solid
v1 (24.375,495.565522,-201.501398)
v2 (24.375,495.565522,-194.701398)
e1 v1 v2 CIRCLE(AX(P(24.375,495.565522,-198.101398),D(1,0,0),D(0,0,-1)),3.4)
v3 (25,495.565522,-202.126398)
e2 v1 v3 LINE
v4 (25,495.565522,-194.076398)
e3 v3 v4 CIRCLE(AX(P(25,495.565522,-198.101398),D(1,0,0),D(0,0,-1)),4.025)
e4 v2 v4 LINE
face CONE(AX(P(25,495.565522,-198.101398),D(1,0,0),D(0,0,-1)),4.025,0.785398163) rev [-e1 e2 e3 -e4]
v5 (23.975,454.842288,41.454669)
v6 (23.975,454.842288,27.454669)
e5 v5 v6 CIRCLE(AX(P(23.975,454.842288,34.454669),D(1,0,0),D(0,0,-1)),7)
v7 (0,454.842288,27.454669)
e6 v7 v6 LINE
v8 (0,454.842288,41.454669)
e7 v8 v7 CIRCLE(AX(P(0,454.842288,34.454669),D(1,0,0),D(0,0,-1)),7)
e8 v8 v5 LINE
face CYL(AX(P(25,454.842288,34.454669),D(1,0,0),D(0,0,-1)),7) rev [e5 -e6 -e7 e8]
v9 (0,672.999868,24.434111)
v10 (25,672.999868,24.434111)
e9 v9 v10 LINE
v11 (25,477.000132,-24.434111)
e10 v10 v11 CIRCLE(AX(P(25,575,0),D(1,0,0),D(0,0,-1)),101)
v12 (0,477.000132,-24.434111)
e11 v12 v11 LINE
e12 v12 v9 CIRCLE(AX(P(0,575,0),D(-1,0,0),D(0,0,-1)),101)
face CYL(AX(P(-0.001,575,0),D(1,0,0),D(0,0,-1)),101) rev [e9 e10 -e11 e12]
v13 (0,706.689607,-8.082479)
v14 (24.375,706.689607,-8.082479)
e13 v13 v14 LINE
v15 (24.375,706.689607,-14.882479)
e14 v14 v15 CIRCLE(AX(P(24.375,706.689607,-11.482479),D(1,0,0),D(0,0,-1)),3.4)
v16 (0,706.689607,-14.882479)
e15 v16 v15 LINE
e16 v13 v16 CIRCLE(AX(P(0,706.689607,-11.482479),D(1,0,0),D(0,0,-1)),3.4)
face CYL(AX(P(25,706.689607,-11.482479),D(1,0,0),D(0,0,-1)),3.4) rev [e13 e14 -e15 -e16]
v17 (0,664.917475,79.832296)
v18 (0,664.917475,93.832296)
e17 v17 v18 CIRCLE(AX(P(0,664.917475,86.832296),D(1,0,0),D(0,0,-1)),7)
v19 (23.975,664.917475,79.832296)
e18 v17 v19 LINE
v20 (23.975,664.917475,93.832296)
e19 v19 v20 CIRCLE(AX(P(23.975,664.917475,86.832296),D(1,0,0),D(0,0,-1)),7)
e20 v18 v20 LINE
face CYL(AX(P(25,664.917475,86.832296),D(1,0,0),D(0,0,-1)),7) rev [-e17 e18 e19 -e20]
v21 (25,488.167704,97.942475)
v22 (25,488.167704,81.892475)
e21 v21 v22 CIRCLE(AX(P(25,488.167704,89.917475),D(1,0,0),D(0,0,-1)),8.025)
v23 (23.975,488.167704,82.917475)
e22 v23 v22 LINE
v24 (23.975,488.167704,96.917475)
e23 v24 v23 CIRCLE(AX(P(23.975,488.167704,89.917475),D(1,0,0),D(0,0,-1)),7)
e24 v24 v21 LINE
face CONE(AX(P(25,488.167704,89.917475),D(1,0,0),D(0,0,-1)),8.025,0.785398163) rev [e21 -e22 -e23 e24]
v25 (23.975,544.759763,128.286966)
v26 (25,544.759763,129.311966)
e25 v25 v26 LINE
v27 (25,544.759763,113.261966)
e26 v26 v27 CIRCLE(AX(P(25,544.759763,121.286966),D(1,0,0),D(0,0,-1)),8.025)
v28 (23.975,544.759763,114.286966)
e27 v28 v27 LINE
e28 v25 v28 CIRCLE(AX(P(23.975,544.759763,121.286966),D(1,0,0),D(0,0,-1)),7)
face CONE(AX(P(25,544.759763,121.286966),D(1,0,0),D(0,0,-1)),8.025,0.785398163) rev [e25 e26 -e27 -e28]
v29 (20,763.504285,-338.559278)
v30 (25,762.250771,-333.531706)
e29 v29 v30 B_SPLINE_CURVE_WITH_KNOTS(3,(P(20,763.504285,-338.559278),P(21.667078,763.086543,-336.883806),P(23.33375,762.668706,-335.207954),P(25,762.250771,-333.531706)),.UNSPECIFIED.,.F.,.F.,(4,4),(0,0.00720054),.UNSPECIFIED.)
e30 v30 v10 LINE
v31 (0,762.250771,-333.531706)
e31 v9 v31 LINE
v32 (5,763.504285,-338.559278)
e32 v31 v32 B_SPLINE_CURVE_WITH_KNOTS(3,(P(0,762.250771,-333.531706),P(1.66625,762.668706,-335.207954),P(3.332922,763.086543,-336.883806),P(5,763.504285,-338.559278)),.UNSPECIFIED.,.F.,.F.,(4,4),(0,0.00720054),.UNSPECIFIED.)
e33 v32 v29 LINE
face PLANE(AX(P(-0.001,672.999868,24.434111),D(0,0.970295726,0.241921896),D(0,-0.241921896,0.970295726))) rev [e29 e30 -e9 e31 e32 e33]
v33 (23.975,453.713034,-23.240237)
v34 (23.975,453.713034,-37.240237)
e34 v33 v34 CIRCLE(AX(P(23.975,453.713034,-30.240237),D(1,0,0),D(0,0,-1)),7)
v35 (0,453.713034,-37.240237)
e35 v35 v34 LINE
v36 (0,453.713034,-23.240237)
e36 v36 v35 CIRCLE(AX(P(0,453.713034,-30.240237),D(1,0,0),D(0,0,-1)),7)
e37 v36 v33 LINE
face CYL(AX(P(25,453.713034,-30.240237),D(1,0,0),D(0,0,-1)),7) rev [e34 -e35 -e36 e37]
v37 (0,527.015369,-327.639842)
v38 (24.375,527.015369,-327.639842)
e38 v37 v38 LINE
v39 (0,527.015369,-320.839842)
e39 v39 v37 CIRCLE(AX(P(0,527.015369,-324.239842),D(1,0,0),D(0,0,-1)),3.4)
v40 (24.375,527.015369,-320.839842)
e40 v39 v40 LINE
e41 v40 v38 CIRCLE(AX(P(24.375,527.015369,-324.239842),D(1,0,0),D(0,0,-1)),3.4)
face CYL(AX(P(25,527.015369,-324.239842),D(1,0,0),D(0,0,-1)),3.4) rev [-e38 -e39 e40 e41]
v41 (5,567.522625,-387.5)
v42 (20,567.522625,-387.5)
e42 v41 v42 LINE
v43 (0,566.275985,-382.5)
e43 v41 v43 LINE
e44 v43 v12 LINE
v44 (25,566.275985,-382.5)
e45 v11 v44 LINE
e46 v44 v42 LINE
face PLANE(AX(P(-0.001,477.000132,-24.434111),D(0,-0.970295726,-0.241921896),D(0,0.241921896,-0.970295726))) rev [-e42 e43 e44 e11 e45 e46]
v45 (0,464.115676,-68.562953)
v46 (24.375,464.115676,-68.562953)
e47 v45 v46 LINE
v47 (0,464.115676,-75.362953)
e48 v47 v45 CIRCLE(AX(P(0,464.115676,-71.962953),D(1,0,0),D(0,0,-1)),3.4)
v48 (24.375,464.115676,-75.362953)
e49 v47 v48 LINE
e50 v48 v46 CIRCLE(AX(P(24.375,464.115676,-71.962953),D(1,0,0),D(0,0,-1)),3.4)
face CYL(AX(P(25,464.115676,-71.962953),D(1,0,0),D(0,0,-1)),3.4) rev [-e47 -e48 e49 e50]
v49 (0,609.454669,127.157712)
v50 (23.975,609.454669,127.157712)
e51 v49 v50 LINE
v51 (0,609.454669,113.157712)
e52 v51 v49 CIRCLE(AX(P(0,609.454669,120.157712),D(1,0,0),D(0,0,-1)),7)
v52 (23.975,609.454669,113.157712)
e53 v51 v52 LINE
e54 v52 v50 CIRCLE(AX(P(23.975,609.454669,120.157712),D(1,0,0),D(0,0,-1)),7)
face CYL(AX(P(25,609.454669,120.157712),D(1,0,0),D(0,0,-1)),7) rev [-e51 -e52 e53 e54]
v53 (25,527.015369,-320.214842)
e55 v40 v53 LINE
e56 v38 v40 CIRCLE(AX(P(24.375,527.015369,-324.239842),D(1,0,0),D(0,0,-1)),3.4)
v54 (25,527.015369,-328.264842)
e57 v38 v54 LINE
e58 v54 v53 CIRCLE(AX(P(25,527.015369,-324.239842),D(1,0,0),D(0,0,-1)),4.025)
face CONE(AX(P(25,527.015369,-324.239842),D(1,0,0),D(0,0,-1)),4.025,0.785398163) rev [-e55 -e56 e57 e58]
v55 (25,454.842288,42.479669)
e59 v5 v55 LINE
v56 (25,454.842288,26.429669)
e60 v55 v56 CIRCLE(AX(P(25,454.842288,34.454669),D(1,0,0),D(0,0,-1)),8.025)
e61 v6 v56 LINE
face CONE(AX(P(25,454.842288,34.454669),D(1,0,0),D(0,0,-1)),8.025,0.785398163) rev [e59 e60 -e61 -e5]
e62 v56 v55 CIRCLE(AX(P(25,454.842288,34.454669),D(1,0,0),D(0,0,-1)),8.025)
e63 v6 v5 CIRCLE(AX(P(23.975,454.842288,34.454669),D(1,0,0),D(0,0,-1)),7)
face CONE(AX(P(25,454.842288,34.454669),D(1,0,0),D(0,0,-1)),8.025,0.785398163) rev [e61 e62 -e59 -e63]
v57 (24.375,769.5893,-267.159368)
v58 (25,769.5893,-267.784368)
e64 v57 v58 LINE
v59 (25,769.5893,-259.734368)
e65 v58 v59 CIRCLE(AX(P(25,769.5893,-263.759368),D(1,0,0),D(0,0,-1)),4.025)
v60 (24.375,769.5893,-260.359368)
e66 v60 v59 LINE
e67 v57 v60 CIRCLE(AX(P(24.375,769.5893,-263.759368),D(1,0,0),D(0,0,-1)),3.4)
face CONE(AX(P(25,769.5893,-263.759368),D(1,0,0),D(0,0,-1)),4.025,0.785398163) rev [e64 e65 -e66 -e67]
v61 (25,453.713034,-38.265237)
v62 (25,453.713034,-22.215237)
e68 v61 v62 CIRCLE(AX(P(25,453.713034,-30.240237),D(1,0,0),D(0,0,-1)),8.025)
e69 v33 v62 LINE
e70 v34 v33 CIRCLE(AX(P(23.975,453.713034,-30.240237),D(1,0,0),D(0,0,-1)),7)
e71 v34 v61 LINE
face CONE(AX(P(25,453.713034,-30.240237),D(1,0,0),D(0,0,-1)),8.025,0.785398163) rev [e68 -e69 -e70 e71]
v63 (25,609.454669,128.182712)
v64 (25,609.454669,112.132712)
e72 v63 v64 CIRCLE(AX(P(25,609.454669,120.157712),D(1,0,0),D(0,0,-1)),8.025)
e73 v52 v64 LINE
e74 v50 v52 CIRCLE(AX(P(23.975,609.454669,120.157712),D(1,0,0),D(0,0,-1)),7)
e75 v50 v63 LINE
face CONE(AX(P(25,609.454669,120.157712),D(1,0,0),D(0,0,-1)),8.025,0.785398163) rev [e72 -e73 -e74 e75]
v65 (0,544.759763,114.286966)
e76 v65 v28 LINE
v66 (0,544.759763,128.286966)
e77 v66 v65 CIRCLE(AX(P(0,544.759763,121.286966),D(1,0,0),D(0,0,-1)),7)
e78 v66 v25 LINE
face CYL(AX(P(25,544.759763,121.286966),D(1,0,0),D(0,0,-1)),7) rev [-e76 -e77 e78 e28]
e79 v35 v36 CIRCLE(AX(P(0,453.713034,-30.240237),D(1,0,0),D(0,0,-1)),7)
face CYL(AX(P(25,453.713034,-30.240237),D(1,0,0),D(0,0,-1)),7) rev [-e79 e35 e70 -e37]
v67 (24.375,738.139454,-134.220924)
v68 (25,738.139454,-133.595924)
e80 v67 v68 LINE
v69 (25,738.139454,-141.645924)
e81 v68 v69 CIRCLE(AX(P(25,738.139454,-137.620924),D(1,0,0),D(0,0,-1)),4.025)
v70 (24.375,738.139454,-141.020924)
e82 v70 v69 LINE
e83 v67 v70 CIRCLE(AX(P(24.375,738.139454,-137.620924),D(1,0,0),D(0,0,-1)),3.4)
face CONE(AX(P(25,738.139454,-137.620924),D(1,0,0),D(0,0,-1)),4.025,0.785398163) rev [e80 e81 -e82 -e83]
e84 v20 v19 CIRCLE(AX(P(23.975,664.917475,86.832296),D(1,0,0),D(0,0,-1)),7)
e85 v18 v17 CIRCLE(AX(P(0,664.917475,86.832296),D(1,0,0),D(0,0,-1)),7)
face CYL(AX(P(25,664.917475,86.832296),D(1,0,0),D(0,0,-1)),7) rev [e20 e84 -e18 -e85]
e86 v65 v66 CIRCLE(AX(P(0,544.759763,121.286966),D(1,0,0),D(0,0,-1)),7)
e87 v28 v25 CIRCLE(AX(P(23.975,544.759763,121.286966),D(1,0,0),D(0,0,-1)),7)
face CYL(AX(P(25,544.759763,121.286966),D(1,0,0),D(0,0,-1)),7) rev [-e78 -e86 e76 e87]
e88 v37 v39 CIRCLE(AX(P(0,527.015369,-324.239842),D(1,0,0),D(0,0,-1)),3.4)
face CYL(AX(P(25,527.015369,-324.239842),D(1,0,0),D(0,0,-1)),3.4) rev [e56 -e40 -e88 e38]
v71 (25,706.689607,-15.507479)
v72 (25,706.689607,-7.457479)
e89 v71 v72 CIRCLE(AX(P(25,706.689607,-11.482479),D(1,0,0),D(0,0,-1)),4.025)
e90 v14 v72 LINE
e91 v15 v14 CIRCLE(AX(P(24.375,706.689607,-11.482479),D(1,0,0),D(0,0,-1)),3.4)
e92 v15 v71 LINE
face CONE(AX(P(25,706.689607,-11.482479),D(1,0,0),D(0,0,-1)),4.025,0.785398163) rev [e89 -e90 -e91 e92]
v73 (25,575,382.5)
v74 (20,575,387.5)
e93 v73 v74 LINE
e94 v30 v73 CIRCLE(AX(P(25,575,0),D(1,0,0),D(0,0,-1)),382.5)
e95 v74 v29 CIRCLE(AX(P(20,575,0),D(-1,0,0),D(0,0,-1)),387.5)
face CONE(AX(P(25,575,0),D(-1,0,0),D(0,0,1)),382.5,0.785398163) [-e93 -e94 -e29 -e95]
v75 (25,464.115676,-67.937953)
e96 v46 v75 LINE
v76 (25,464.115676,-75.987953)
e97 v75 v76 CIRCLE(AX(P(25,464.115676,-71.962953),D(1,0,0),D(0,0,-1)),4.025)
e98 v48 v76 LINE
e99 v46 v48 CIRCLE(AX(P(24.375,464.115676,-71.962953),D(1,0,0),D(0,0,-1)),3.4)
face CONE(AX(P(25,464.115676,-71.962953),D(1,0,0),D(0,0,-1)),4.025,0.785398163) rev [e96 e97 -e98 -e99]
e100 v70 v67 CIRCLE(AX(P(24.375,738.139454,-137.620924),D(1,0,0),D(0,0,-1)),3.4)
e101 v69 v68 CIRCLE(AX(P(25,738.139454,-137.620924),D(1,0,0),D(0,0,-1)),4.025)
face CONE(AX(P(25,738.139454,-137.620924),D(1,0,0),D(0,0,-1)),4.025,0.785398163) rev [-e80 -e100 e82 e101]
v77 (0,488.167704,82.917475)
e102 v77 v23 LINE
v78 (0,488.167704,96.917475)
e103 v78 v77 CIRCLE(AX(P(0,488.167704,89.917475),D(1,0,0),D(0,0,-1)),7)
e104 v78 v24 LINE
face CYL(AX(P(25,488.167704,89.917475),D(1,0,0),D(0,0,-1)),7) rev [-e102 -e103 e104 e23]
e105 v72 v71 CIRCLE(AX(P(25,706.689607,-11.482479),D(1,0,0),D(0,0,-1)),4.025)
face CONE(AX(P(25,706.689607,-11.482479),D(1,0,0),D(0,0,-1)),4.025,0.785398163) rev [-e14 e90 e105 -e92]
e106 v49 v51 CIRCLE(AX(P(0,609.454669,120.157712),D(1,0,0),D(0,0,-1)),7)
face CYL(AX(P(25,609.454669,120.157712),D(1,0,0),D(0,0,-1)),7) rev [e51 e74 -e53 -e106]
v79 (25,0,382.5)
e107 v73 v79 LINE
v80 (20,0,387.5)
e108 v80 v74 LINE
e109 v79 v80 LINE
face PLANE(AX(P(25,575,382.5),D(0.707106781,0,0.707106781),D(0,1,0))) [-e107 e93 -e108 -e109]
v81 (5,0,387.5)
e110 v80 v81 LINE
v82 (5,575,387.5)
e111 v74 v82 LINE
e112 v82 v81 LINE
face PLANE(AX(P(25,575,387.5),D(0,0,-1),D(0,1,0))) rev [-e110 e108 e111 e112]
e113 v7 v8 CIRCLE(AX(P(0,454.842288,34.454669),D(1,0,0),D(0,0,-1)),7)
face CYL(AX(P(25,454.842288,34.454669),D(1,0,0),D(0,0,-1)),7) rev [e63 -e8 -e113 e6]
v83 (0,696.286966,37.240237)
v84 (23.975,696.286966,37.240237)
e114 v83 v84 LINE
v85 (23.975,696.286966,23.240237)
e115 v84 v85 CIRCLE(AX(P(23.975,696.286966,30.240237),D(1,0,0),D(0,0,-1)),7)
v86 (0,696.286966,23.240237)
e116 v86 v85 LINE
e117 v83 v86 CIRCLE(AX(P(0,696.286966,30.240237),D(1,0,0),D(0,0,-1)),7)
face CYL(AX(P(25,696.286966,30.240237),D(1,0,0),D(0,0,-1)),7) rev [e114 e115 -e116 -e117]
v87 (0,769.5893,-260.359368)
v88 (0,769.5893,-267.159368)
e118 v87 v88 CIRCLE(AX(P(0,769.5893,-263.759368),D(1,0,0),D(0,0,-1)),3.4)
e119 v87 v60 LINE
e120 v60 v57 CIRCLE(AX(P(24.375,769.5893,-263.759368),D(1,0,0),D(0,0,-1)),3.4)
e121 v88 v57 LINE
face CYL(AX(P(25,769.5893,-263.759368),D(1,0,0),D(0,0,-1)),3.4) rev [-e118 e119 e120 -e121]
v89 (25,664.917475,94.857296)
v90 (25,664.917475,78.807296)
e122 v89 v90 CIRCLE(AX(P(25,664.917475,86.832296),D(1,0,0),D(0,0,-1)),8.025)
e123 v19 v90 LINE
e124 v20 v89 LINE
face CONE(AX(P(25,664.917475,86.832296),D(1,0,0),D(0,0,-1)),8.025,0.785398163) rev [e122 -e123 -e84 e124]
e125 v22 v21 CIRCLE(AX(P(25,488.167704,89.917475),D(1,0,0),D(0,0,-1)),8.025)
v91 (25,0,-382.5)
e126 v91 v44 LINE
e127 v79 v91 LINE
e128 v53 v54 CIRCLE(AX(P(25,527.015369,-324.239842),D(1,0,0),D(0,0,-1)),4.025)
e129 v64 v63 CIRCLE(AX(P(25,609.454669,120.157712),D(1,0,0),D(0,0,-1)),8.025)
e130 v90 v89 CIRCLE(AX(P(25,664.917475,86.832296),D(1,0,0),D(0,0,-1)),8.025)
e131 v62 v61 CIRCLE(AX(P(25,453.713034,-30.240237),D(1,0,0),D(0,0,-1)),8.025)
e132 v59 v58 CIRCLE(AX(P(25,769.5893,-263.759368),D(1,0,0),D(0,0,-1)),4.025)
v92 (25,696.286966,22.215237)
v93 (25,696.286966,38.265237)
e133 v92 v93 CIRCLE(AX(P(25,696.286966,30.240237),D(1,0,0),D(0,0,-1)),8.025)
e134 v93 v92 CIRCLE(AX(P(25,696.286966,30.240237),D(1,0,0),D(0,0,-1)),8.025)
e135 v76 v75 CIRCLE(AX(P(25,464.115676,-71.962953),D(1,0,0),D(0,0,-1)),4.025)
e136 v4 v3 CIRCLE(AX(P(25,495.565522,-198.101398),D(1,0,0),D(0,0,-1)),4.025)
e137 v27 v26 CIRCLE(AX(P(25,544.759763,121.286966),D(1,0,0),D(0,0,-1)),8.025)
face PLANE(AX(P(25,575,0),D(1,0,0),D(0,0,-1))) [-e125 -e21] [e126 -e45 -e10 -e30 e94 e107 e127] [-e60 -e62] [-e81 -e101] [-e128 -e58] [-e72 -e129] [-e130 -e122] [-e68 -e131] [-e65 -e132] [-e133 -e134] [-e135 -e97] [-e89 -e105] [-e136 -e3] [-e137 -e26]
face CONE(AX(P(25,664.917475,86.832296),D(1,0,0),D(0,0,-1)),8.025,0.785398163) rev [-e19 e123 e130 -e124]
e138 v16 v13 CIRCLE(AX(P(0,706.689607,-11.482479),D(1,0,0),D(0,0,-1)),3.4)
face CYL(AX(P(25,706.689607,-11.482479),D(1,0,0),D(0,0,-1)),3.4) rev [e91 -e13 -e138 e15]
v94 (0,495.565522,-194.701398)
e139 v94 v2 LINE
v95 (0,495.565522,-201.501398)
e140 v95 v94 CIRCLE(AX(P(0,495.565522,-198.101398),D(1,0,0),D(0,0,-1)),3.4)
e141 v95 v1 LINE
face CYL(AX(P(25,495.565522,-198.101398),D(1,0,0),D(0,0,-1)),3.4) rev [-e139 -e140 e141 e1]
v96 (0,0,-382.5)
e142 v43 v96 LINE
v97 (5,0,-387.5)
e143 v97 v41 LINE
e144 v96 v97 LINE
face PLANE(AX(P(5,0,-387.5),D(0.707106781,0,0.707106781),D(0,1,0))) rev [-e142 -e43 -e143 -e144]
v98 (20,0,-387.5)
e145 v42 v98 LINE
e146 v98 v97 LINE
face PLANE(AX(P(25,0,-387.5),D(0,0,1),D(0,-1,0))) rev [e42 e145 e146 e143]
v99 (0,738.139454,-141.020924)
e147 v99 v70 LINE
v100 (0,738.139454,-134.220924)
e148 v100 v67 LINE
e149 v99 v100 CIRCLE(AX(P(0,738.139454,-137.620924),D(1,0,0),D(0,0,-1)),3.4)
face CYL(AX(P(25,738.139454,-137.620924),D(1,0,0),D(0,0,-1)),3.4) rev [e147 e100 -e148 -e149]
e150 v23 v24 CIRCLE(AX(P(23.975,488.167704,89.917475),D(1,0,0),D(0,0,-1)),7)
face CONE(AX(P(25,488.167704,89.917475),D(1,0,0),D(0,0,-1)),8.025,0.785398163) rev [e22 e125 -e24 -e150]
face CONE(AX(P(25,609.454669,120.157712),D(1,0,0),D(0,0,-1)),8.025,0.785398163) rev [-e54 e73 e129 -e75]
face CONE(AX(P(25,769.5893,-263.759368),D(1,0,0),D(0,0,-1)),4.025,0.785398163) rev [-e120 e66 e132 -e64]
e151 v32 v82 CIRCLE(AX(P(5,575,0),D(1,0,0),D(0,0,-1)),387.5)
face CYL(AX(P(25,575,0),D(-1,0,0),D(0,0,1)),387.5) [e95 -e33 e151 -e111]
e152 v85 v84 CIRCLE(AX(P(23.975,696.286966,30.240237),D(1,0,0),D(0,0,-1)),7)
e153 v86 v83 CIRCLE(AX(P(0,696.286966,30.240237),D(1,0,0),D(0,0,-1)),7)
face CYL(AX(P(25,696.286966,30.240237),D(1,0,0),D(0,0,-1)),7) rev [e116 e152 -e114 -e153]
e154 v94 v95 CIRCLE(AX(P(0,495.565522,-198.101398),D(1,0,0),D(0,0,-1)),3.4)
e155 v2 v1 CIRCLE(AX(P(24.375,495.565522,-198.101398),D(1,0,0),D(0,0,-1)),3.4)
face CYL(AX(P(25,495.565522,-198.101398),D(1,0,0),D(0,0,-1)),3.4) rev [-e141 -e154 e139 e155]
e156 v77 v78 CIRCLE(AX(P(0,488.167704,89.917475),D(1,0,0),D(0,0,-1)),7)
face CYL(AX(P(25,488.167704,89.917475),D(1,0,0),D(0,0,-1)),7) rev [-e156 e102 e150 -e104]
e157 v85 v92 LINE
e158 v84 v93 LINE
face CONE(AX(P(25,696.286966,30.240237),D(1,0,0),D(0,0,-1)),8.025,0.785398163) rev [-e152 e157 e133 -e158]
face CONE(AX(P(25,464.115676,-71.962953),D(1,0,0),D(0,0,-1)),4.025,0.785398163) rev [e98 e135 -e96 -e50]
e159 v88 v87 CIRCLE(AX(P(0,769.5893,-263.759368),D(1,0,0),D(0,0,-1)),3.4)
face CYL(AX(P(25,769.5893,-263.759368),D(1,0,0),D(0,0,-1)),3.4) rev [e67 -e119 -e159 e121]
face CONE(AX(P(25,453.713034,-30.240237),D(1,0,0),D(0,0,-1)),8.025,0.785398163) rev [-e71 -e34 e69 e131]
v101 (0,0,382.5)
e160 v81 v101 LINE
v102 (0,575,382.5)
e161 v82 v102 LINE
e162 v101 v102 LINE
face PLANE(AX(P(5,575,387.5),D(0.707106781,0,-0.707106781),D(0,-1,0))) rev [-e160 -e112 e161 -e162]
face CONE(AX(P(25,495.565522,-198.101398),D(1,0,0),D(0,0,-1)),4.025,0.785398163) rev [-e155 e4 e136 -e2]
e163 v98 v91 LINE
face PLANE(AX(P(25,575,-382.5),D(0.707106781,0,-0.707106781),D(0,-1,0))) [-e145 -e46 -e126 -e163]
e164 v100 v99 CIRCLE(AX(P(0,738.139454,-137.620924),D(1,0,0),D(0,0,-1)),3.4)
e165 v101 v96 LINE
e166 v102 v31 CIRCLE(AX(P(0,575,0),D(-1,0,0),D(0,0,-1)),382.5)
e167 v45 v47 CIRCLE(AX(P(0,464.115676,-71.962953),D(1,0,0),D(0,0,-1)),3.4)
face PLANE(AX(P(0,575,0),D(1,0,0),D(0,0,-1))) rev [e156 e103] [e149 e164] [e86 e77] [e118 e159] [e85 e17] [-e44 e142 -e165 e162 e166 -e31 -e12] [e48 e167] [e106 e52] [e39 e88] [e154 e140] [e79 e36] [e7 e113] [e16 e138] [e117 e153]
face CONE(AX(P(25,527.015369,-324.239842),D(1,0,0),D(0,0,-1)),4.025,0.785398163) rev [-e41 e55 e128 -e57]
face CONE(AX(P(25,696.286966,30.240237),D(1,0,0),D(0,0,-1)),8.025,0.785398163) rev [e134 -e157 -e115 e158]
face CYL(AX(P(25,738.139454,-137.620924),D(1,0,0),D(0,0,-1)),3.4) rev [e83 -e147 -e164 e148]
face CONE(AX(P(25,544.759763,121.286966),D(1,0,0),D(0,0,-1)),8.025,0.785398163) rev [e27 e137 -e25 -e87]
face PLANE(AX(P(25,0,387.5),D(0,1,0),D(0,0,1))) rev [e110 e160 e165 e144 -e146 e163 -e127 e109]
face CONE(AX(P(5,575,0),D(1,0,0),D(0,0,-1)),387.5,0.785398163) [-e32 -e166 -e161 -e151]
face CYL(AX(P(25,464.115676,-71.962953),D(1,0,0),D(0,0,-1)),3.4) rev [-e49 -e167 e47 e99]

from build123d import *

# Parameters (mm, degrees)
BOSS_EXTRUDE1_DEPTH          = 25
CUT_EXTRUDE1_REACH           = 1039.876
M16_TAPPED_HOLE1_D           = 14
M16_TAPPED_HOLE1_CSINK_D     = 16.05
M16_TAPPED_HOLE1_CSINK_ANGLE = 90
CIRPATTERN1_COUNT            = 12
M8_TAPPED_HOLE1_D            = 6.8
M8_TAPPED_HOLE1_CSINK_D      = 8.05
M8_TAPPED_HOLE1_CSINK_ANGLE  = 90
LPATTERN1_COUNT              = 3
LPATTERN1_PITCH              = 130
MIRROR1_COPY_1_D             = 6.8
MIRROR1_COPY_1_CSINK_D       = 8.05
MIRROR1_COPY_1_CSINK_ANGLE   = 90
MIRROR1_COPY_2_D             = 6.8
MIRROR1_COPY_2_CSINK_D       = 8.05
MIRROR1_COPY_2_CSINK_ANGLE   = 90
CHAMFER1_SIZE                = 5


with BuildPart() as part:
    # Sketch1 → Boss-Extrude1 (new body)
    with BuildSketch(Plane(origin=(0, 0, 0), x_dir=(0, 0, -1), z_dir=(1, 0, 0))):
        with BuildLine():
            Line((-387.5, 575), (-387.5, 0))
            Line((-387.5, 0), (387.5, 0))
            Line((387.5, 0), (387.5, 575))
            ThreePointArc((387.5, 575), (0, 962.5), (-387.5, 575))
        make_face()
    extrude(amount=BOSS_EXTRUDE1_DEPTH)

    # Sketch2 → Cut-Extrude1 (cut, up to next)
    with BuildSketch(Plane(origin=(25, 0, 0), x_dir=(0, 0, -1), z_dir=(1, 0, 0)), mode=Mode.PRIVATE) as cut_extrude1_sk1:
        with BuildLine():
            Line((-24.434111456, 672.999868354), (338.559277668, 763.504285109))
            ThreePointArc((338.559277668, 763.504285109), (375.065307711, 672.37692207), (387.5, 575))
            Line((387.5, 575), (387.5, 567.522624537))
            Line((387.5, 567.522624537), (24.434111456, 477.000131646))
            ThreePointArc((24.434111456, 477.000131646), (-97.999868354, 550.565888544), (-24.434111456, 672.999868354))
        make_face()
    cut_extrude1_tool1 = extrude(cut_extrude1_sk1.sketch, amount=-CUT_EXTRUDE1_REACH, mode=Mode.PRIVATE) & part.part
    add(cut_extrude1_tool1.solids().sort_by_distance((25, 611.611981, -146.843429))[0], mode=Mode.SUBTRACT)

    # M16 Tapped Hole1 (through all)
    with Locations(Plane(origin=(25, 696.286965784, 30.24023695), x_dir=(0, 0, 1), z_dir=(1, 0, 0))):
        with Locations((0, 0)):
            m16_tapped_hole1 = CounterSinkHole(M16_TAPPED_HOLE1_D / 2, M16_TAPPED_HOLE1_CSINK_D / 2, counter_sink_angle=M16_TAPPED_HOLE1_CSINK_ANGLE)

    # CirPattern1: M16 Tapped Hole1 ×12 about axis, 5 skipped
    cirpattern1_axis = Axis((-0.001, 575, 0), (-1, 0, 0))
    add([m16_tapped_hole1.rotate(cirpattern1_axis, i * 360 / CIRPATTERN1_COUNT) for i in range(1, CIRPATTERN1_COUNT) if i not in (1, 2, 3, 4, 5)], mode=Mode.SUBTRACT)

    # M8 Tapped Hole1 (through all)
    with Locations(Plane(origin=(25, 706.689607295, -11.48247928), x_dir=(0, 0, 1), z_dir=(1, 0, 0))):
        with Locations((0, 0)):
            m8_tapped_hole1 = CounterSinkHole(M8_TAPPED_HOLE1_D / 2, M8_TAPPED_HOLE1_CSINK_D / 2, counter_sink_angle=M8_TAPPED_HOLE1_CSINK_ANGLE)

    # LPattern1: M8 Tapped Hole1 ×3
    with Locations(*[Vector(0, 0.24192189559966076, -0.9702957262759982) * (i * LPATTERN1_PITCH) for i in range(1, LPATTERN1_COUNT)]):
        add(m8_tapped_hole1, mode=Mode.SUBTRACT)

    # Mirror1: M8 Tapped Hole1 across plane
    add(m8_tapped_hole1.mirror(Plane(origin=(0, 541.347432947, 134.973074301), x_dir=(0, -0.24192189559966135, 0.970295726275998), z_dir=(0, 0.9702957262759981, 0.24192189559966135))), mode=Mode.SUBTRACT)

    # Mirror1 copy 1 (through all)
    with Locations(Plane(origin=(25, 495.565522155, -198.101397596), x_dir=(0, -0.4694715627858792, 0.8829475928589331), z_dir=(1, 0, 0))):
        with Locations((0, 0)):
            CounterSinkHole(MIRROR1_COPY_1_D / 2, MIRROR1_COPY_1_CSINK_D / 2, counter_sink_angle=MIRROR1_COPY_1_CSINK_ANGLE)

    # Mirror1 copy 2 (through all)
    with Locations(Plane(origin=(25, 527.015368582, -324.239842012), x_dir=(0, -0.4694715627858792, 0.8829475928589331), z_dir=(1, 0, 0))):
        with Locations((0, 0)):
            CounterSinkHole(MIRROR1_COPY_2_D / 2, MIRROR1_COPY_2_CSINK_D / 2, counter_sink_angle=MIRROR1_COPY_2_CSINK_ANGLE)

    # Chamfer1
    chamfer1_edges = [part.edges().sort_by_distance(p)[0] for p in [
        (0, 950.065307711, 97.37692207),
        (25, 950.065307711, 97.37692207),
        (25, 283.761312269, -387.5),
        (0, 283.761312269, -387.5),
        (0, 287.5, 387.5),
        (25, 287.5, 387.5),
    ]]
    chamfer(chamfer1_edges, length=CHAMFER1_SIZE)


solid = part.part
